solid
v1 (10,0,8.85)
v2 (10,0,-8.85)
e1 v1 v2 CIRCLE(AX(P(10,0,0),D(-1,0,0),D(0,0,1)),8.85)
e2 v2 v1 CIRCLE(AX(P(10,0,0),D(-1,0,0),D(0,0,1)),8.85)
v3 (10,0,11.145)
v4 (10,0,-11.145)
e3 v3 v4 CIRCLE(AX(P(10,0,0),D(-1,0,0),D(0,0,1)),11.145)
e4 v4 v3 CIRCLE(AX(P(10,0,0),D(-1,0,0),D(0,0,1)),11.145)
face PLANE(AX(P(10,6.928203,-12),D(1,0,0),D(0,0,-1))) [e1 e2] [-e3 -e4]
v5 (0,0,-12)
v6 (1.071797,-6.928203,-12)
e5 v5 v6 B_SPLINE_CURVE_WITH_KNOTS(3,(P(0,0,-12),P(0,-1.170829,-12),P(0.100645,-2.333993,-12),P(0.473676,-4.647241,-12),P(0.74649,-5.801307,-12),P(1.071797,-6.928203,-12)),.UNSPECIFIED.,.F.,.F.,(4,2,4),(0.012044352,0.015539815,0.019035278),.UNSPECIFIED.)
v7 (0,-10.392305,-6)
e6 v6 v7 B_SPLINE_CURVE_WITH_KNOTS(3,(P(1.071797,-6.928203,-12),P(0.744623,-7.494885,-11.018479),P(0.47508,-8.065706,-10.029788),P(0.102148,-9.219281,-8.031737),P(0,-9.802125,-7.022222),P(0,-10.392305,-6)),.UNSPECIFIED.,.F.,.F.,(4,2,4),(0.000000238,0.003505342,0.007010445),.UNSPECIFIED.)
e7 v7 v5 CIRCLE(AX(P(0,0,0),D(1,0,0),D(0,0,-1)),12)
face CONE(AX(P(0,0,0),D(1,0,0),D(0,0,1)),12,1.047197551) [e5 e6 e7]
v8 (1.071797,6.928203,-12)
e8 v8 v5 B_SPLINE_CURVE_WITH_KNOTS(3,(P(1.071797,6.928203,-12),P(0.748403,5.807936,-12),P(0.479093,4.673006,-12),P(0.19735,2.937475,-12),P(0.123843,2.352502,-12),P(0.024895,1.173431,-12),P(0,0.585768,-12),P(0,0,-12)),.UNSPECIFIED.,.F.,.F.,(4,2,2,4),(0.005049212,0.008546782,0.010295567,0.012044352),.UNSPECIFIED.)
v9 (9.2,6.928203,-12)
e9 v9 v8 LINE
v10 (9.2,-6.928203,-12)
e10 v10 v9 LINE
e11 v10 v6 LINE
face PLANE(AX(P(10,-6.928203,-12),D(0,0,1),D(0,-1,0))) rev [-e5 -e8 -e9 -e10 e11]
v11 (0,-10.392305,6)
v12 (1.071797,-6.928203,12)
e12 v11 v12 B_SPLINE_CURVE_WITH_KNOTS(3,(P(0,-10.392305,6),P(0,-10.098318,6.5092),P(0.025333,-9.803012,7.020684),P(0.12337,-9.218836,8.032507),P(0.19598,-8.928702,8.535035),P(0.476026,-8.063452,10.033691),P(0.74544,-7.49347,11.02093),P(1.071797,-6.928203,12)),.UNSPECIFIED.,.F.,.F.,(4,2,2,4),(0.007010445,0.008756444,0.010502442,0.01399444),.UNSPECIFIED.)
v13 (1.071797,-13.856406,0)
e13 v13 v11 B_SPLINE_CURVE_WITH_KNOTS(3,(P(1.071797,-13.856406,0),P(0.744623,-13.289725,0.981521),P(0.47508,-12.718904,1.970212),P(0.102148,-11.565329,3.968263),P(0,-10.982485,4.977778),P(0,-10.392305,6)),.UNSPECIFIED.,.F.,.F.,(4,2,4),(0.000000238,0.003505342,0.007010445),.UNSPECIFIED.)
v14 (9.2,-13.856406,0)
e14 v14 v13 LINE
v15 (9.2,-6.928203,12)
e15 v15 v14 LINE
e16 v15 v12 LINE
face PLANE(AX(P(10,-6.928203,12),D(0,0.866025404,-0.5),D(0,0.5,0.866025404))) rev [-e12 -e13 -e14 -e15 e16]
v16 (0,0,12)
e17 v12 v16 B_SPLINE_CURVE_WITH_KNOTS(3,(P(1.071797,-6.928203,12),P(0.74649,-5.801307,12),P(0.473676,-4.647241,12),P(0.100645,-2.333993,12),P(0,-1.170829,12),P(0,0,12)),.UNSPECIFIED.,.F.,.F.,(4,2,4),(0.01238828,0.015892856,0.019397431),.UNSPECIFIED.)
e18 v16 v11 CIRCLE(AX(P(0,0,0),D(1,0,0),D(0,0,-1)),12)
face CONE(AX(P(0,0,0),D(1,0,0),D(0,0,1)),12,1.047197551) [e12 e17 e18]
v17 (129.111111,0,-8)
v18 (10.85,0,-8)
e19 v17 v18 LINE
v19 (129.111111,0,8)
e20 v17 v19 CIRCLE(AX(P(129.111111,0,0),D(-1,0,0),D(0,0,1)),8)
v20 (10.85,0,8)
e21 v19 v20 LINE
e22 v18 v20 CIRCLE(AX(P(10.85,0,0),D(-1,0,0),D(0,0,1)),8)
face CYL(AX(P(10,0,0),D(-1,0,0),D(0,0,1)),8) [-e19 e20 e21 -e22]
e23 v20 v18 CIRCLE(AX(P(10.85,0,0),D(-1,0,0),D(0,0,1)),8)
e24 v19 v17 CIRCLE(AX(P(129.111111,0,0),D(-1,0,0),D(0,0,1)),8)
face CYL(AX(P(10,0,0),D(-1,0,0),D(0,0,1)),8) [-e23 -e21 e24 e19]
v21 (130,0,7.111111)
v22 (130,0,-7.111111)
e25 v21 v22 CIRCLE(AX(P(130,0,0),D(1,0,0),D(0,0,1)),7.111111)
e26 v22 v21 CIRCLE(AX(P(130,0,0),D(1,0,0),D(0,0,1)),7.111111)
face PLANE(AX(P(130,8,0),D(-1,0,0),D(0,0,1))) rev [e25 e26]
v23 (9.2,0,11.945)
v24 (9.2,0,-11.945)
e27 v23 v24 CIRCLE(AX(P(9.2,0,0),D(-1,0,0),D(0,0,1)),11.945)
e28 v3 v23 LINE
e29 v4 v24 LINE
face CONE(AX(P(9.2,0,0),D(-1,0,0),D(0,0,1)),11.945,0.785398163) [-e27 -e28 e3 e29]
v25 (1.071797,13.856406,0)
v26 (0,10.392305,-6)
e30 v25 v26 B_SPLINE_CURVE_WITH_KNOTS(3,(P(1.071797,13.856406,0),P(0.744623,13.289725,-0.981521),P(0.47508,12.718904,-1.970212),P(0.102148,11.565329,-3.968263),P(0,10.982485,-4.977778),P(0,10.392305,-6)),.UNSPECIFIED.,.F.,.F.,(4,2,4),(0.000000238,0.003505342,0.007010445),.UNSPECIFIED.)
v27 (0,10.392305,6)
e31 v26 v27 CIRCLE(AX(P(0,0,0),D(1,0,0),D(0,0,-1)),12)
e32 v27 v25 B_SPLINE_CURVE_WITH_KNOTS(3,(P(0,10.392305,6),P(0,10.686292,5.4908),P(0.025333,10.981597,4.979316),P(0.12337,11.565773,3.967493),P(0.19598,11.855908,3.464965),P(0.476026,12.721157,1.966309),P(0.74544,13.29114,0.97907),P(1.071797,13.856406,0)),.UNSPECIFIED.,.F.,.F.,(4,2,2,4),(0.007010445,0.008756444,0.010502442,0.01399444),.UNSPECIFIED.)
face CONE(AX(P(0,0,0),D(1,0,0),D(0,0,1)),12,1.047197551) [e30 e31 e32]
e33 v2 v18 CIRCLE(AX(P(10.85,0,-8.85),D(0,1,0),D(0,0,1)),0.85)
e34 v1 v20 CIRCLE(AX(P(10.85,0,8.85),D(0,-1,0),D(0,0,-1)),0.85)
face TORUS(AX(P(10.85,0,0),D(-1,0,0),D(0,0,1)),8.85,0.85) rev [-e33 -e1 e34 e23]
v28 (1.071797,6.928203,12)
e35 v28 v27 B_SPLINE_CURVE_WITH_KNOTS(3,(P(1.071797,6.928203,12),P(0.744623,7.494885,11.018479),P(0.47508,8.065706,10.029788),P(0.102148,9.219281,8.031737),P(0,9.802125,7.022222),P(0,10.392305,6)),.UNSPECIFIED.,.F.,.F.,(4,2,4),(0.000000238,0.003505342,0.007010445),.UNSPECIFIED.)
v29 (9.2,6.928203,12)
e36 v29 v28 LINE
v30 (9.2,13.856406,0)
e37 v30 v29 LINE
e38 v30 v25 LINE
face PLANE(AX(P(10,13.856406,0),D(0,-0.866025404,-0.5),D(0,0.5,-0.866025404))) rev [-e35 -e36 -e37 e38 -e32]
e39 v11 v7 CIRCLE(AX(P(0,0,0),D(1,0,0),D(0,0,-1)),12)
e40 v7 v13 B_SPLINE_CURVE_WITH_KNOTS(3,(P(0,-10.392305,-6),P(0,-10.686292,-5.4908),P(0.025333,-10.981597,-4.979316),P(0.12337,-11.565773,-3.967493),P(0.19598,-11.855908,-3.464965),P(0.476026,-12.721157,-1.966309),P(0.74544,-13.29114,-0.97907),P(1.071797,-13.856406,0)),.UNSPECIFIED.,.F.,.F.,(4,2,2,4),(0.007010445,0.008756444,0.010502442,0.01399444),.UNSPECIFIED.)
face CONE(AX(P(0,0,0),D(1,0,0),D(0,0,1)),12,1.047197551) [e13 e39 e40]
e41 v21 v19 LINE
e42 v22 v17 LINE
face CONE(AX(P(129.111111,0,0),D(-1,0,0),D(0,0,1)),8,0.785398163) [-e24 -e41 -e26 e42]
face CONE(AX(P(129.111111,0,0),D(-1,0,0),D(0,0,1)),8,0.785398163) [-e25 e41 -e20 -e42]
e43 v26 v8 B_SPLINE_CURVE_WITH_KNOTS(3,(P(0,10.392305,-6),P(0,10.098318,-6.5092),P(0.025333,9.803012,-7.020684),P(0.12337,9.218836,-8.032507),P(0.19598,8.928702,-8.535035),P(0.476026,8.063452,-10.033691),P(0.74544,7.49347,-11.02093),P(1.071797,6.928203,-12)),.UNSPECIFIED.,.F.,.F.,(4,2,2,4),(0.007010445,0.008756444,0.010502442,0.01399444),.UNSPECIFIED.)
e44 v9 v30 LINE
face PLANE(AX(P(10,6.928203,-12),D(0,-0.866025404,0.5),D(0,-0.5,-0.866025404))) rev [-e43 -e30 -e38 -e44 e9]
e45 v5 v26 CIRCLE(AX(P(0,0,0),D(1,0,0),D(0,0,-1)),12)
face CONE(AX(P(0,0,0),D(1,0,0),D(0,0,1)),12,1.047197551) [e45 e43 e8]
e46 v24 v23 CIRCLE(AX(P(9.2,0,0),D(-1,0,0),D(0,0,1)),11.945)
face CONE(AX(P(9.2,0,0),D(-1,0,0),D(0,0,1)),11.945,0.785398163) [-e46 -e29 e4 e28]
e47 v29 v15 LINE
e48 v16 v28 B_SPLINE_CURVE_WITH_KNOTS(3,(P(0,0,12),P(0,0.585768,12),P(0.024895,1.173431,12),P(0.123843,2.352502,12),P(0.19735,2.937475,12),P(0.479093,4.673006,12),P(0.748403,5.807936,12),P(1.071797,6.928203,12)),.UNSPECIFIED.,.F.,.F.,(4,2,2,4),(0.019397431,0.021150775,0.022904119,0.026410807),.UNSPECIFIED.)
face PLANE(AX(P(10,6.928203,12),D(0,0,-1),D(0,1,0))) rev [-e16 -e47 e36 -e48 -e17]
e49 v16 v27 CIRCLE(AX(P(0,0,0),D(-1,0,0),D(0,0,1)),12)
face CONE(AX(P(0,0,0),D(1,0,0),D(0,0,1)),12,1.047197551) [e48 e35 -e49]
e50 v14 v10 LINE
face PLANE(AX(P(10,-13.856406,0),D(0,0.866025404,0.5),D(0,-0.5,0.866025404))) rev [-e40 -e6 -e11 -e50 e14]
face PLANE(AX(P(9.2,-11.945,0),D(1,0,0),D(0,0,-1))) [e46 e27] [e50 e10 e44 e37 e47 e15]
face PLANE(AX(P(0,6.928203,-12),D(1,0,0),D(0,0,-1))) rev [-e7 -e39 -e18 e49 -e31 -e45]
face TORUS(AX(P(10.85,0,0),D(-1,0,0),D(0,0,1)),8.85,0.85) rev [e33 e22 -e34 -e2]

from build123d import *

# Parameters (mm, degrees)
BOSS_EXTRUDE1_DEPTH = 10
SKETCH4_R           = 26.75
SKETCH4_R_2         = 12
CUT_EXTRUDE1_DEPTH  = 1.25
CUT_EXTRUDE1_DRAFT  = -60
CHAMFER2_SIZE       = 0.888888889


with BuildPart() as part:
    # Sketch3 → Boss-Extrude1 (new body)
    with BuildSketch(Plane(origin=(0, 0, 0), x_dir=(0, 0, -1), z_dir=(1, 0, 0))):
        Polygon((12, 6.92820323), (0, 13.856406461), (-12, 6.92820323), (-12, -6.92820323), (0, -13.856406461), (12, -6.92820323), align=None)
    extrude(amount=BOSS_EXTRUDE1_DEPTH)


with BuildPart() as cut_extrude1_tool:
    # Sketch4 → Cut-Extrude1 (with draft: the straight prism first)
    with BuildSketch(Plane.ZY):
        Circle(SKETCH4_R)
        Circle(SKETCH4_R_2, mode=Mode.SUBTRACT)
    extrude(amount=-CUT_EXTRUDE1_DEPTH)
    # Cut-Extrude1: the draft: its side faces are tilted about the plane it starts from
    cut_extrude1_sides = [cut_extrude1_tool.faces().sort_by_distance(p)[0] for p in [
        (0.625, 0, -26.75),
        (0.625, 0, -12),
    ]]
    draft(cut_extrude1_sides, Plane.ZY, CUT_EXTRUDE1_DRAFT)


with BuildPart() as part_1:
    add(part.part)

    # Cut-Extrude1: cut by cut_extrude1_tool
    add(cut_extrude1_tool.part, mode=Mode.SUBTRACT)

    # Sketch5 → Revolve1 (revolve)
    with BuildSketch(Plane.XY, mode=Mode.PRIVATE) as revolve1_sk:
        with BuildLine():
            Line((10.85, 8), (130, 8))
            Line((130, 8), (130, 0))
            Line((130, 0), (10, 0))
            Line((10, 0), (10, 8.85))
            ThreePointArc((10, 8.85), (10.248959236, 8.248959236), (10.85, 8))
        make_face()
    revolve(revolve1_sk.sketch.rotate(Axis((10, 0, 0), (1, 0, 0)), 90), axis=Axis((10, 0, 0), (1, 0, 0)))

    # Chamfer2
    chamfer2_edges = [part_1.edges().sort_by_distance(p)[0] for p in [
        (130, 0, -8),
    ]]
    chamfer(chamfer2_edges, length=CHAMFER2_SIZE)

    # Sketch7 → Cut-Revolve1 (revolve, cut)
    with BuildSketch(Plane.XY, mode=Mode.PRIVATE) as cut_revolve1_sk:
        Polygon((10, 11.145), (9.2, 11.945), (9.2, 26.75), (10, 26.75), align=None)
    revolve(cut_revolve1_sk.sketch.rotate(Axis((0, 0, 0), (1, 0, 0)), 90), axis=Axis((0, 0, 0), (1, 0, 0)), mode=Mode.SUBTRACT)


solid = part_1.part
